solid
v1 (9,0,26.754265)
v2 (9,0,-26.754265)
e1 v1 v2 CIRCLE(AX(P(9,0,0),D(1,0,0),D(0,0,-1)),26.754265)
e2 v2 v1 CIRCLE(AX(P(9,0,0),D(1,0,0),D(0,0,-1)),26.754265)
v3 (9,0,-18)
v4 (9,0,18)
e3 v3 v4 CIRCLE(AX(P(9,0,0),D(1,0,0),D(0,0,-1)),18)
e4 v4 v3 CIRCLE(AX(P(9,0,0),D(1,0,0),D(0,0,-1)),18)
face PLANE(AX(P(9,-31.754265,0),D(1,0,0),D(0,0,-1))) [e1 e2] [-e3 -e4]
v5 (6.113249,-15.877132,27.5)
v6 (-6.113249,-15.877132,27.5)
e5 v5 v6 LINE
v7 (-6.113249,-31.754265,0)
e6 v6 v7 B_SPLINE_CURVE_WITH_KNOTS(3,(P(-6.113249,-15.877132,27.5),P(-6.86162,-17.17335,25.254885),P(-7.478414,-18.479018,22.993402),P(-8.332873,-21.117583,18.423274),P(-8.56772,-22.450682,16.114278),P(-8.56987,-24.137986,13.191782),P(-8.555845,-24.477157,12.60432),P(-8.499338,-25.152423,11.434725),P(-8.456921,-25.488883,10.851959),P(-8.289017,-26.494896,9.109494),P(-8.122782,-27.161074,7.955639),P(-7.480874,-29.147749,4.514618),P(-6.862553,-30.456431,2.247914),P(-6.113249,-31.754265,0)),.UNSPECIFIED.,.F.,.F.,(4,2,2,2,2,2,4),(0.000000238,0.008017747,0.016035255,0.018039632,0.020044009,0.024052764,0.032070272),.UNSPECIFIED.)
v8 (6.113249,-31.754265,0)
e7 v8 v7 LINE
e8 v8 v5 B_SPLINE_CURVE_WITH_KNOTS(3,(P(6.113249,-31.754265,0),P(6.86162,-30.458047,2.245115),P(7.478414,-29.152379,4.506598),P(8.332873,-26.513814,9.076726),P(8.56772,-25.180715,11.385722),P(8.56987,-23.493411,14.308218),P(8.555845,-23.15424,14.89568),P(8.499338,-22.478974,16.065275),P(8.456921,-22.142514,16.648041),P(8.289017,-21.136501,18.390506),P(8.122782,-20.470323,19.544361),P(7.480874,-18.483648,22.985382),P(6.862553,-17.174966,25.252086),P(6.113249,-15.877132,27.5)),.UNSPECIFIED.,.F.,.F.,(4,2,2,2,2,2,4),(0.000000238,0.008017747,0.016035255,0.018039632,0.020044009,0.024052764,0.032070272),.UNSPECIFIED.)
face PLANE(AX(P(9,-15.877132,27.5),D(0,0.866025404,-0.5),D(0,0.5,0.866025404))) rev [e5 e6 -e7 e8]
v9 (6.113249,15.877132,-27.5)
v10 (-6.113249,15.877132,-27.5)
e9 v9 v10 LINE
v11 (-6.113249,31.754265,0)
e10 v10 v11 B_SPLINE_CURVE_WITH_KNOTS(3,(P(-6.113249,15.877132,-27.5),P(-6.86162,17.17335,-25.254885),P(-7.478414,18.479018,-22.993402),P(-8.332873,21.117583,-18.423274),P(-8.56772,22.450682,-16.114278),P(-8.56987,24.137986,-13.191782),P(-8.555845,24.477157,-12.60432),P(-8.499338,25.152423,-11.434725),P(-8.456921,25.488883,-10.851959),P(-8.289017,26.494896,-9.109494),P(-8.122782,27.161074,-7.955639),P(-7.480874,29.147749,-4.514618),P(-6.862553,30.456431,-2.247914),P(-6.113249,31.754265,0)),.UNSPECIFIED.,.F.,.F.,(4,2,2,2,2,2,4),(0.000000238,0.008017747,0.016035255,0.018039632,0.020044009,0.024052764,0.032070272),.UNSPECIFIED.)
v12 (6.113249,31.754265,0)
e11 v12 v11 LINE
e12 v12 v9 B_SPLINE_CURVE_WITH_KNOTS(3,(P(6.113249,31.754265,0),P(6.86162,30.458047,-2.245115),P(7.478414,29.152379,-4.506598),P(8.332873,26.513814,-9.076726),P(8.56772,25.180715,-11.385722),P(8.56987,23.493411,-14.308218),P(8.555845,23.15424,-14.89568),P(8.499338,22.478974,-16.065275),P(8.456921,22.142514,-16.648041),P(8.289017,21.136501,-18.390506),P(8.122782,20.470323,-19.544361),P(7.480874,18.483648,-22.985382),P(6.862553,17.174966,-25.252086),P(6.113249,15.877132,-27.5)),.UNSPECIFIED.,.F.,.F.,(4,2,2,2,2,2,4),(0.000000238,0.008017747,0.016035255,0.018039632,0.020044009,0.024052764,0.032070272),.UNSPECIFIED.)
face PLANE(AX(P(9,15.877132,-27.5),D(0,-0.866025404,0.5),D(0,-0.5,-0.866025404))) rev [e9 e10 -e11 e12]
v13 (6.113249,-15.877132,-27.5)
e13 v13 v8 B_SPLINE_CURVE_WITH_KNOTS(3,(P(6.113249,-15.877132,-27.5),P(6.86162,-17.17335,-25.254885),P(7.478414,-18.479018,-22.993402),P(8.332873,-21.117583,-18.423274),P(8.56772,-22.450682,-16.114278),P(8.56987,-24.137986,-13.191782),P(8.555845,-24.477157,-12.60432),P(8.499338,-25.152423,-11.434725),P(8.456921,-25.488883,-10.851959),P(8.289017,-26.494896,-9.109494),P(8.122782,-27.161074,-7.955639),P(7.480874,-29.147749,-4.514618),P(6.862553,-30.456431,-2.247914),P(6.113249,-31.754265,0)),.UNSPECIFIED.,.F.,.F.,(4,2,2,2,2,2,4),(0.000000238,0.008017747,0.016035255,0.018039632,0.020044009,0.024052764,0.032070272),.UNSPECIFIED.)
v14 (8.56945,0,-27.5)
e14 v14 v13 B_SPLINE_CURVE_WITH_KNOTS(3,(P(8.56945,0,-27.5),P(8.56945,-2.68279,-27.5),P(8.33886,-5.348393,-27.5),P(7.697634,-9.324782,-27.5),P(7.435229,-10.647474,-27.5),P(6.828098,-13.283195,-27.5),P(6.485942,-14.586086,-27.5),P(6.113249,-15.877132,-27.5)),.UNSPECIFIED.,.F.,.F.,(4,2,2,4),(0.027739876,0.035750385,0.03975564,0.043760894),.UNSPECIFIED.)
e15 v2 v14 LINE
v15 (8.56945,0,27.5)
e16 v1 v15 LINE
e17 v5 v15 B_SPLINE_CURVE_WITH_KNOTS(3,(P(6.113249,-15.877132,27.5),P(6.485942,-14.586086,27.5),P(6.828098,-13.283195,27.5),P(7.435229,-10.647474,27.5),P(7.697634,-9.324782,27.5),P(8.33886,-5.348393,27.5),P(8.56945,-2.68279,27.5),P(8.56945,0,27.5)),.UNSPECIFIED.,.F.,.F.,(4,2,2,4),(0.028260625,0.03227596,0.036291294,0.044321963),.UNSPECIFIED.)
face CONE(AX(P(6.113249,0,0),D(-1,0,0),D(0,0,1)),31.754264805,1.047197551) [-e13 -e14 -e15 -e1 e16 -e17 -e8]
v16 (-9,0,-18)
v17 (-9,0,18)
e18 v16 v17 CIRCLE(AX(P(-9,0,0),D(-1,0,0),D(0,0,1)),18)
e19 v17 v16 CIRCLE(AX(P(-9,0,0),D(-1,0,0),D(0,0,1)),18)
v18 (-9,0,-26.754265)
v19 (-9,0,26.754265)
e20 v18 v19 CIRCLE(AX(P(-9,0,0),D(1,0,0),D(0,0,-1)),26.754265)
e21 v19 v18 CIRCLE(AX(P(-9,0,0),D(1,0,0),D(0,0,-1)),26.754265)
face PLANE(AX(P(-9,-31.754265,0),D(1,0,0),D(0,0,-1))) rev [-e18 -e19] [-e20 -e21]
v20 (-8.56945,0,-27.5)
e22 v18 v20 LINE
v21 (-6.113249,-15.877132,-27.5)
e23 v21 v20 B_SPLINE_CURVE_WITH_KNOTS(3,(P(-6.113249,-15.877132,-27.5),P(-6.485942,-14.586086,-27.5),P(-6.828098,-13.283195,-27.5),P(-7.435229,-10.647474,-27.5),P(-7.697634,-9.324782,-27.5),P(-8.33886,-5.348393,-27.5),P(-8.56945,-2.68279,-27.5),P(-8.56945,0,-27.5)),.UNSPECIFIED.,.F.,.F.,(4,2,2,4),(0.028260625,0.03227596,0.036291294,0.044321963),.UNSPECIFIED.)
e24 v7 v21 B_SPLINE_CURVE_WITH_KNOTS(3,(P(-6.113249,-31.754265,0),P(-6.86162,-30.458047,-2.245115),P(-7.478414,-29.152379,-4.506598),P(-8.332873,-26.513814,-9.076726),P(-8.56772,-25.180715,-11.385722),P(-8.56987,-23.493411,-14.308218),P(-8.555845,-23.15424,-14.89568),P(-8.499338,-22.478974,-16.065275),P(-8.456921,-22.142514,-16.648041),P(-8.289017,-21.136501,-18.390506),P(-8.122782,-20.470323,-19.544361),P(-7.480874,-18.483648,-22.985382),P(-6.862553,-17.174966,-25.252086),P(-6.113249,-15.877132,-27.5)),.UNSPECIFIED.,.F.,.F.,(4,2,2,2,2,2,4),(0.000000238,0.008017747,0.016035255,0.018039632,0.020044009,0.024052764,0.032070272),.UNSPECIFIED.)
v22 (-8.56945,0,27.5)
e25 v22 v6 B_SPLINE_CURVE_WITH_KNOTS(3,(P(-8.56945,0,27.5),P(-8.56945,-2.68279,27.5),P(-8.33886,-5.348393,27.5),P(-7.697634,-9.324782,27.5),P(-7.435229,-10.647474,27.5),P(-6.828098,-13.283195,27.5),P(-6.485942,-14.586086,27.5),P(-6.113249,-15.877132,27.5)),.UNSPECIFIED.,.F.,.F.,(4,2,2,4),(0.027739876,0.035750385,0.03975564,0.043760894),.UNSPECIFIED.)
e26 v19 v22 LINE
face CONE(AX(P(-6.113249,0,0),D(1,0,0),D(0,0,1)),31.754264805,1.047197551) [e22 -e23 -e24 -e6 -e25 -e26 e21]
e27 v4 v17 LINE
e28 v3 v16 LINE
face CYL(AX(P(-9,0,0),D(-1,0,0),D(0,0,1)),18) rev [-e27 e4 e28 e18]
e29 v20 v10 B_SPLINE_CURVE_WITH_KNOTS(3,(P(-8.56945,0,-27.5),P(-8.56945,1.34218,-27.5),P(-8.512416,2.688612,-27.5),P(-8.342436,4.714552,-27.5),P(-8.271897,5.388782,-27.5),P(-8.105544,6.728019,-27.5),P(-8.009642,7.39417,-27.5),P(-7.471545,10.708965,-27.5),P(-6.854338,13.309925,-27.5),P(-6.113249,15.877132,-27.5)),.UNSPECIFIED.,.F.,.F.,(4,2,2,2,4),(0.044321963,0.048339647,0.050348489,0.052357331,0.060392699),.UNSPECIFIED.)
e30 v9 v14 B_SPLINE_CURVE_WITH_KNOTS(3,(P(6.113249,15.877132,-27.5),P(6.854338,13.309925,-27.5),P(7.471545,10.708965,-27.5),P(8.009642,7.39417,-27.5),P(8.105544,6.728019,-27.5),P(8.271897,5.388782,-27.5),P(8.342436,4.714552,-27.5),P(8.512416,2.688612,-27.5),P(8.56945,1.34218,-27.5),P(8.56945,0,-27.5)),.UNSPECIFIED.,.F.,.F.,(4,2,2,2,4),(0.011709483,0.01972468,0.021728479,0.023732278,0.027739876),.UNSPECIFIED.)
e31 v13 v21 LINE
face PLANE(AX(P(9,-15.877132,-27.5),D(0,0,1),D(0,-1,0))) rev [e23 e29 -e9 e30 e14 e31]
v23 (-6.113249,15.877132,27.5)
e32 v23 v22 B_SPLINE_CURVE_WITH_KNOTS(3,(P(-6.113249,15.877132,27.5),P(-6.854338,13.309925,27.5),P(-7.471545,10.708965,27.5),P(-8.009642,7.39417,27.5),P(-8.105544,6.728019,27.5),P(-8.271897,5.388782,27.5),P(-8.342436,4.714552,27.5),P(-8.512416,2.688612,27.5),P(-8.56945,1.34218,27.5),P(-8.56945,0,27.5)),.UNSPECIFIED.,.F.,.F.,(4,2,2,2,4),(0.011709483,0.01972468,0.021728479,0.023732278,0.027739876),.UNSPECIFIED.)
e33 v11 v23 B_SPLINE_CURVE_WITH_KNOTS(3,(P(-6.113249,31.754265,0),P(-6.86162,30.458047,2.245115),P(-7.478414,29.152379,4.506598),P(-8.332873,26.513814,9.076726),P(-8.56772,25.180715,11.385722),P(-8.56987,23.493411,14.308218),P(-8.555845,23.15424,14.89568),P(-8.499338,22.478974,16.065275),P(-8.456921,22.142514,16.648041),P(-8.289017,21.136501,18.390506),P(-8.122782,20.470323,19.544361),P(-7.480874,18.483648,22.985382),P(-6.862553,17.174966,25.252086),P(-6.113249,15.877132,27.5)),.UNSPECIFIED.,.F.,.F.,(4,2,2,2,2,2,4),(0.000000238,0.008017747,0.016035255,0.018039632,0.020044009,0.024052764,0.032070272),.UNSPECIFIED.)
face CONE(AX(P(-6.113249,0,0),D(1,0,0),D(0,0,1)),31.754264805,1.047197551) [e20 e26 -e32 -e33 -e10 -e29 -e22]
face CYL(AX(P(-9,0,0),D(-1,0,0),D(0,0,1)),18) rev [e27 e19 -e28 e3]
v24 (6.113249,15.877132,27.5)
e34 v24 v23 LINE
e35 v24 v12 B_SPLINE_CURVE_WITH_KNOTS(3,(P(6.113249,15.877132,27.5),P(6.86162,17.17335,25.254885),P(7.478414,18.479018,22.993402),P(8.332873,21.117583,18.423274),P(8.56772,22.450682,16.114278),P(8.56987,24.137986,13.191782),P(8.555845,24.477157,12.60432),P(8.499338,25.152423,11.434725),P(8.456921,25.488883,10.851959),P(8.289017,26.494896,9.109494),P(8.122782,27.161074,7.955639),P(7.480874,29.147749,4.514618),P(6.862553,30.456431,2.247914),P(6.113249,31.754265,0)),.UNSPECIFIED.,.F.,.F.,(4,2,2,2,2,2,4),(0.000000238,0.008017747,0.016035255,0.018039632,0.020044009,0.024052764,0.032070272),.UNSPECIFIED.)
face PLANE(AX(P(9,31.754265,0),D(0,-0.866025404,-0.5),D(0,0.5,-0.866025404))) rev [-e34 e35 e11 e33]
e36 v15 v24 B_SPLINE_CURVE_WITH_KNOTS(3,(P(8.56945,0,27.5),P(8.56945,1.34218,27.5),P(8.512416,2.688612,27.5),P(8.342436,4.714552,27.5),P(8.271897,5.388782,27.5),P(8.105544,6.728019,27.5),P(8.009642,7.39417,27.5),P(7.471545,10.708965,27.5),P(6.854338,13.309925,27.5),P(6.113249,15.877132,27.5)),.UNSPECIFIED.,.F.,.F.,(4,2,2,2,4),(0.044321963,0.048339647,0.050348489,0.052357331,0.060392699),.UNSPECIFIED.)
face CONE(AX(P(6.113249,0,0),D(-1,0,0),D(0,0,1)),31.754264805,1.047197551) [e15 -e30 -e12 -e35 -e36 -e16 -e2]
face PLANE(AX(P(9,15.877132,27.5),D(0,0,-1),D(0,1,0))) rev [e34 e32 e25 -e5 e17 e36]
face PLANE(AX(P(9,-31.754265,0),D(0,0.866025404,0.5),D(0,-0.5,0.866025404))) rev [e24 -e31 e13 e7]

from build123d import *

# Parameters (mm, degrees)
EXTRUDE1_DEPTH      = 9
EXTRUDE1_DEPTH_BACK = 9


with BuildPart() as part:
    # Sketch1 → Extrude1 (new, two sides: drawn at the far end of the back side and taken through both)
    with BuildSketch(Plane(origin=(0, 0, 0), x_dir=(0, 0, -1), z_dir=(1, 0, 0)).offset(-EXTRUDE1_DEPTH_BACK)):
        Polygon((0, -31.754264805), (27.5, -15.877132403), (27.5, 15.877132403), (0, 31.754264805), (-27.5, 15.877132403), (-27.5, -15.877132403), align=None)
    extrude(amount=EXTRUDE1_DEPTH + EXTRUDE1_DEPTH_BACK)

    # Sketch4 → M36x2.0 Tapped Hole1 (revolve, cut)
    with BuildSketch(Plane(origin=(-9, 0, 0), x_dir=(0, 0, 1), z_dir=(0, 1, 0))):
        Polygon((0, 0), (0, 88.214630523), (17, 78), (17, 72), (18, 72), (18, 0), align=None)
    revolve(axis=Axis((-15.35, 0, 0), (1, 0, 0)), mode=Mode.SUBTRACT)

    # Sketch2 → Cut-Revolve1 (revolve, cut)
    with BuildSketch(Plane.XY, mode=Mode.PRIVATE) as cut_revolve1_sk:
        Polygon((9, 31.754264805), (6.113248654, 31.754264805), (9, 26.754264805), align=None)
    cut_revolve1 = revolve(cut_revolve1_sk.sketch.rotate(Axis((-9, 0, 0), (-1, 0, 0)), 240.000000138), axis=Axis((-9, 0, 0), (-1, 0, 0)), mode=Mode.SUBTRACT)

    # Mirror1: Cut-Revolve1 across plane
    add(cut_revolve1.mirror(Plane(origin=(0, 0, 0), x_dir=(0, 0, 1), z_dir=(1, 0, 0))), mode=Mode.SUBTRACT)


solid = part.part
